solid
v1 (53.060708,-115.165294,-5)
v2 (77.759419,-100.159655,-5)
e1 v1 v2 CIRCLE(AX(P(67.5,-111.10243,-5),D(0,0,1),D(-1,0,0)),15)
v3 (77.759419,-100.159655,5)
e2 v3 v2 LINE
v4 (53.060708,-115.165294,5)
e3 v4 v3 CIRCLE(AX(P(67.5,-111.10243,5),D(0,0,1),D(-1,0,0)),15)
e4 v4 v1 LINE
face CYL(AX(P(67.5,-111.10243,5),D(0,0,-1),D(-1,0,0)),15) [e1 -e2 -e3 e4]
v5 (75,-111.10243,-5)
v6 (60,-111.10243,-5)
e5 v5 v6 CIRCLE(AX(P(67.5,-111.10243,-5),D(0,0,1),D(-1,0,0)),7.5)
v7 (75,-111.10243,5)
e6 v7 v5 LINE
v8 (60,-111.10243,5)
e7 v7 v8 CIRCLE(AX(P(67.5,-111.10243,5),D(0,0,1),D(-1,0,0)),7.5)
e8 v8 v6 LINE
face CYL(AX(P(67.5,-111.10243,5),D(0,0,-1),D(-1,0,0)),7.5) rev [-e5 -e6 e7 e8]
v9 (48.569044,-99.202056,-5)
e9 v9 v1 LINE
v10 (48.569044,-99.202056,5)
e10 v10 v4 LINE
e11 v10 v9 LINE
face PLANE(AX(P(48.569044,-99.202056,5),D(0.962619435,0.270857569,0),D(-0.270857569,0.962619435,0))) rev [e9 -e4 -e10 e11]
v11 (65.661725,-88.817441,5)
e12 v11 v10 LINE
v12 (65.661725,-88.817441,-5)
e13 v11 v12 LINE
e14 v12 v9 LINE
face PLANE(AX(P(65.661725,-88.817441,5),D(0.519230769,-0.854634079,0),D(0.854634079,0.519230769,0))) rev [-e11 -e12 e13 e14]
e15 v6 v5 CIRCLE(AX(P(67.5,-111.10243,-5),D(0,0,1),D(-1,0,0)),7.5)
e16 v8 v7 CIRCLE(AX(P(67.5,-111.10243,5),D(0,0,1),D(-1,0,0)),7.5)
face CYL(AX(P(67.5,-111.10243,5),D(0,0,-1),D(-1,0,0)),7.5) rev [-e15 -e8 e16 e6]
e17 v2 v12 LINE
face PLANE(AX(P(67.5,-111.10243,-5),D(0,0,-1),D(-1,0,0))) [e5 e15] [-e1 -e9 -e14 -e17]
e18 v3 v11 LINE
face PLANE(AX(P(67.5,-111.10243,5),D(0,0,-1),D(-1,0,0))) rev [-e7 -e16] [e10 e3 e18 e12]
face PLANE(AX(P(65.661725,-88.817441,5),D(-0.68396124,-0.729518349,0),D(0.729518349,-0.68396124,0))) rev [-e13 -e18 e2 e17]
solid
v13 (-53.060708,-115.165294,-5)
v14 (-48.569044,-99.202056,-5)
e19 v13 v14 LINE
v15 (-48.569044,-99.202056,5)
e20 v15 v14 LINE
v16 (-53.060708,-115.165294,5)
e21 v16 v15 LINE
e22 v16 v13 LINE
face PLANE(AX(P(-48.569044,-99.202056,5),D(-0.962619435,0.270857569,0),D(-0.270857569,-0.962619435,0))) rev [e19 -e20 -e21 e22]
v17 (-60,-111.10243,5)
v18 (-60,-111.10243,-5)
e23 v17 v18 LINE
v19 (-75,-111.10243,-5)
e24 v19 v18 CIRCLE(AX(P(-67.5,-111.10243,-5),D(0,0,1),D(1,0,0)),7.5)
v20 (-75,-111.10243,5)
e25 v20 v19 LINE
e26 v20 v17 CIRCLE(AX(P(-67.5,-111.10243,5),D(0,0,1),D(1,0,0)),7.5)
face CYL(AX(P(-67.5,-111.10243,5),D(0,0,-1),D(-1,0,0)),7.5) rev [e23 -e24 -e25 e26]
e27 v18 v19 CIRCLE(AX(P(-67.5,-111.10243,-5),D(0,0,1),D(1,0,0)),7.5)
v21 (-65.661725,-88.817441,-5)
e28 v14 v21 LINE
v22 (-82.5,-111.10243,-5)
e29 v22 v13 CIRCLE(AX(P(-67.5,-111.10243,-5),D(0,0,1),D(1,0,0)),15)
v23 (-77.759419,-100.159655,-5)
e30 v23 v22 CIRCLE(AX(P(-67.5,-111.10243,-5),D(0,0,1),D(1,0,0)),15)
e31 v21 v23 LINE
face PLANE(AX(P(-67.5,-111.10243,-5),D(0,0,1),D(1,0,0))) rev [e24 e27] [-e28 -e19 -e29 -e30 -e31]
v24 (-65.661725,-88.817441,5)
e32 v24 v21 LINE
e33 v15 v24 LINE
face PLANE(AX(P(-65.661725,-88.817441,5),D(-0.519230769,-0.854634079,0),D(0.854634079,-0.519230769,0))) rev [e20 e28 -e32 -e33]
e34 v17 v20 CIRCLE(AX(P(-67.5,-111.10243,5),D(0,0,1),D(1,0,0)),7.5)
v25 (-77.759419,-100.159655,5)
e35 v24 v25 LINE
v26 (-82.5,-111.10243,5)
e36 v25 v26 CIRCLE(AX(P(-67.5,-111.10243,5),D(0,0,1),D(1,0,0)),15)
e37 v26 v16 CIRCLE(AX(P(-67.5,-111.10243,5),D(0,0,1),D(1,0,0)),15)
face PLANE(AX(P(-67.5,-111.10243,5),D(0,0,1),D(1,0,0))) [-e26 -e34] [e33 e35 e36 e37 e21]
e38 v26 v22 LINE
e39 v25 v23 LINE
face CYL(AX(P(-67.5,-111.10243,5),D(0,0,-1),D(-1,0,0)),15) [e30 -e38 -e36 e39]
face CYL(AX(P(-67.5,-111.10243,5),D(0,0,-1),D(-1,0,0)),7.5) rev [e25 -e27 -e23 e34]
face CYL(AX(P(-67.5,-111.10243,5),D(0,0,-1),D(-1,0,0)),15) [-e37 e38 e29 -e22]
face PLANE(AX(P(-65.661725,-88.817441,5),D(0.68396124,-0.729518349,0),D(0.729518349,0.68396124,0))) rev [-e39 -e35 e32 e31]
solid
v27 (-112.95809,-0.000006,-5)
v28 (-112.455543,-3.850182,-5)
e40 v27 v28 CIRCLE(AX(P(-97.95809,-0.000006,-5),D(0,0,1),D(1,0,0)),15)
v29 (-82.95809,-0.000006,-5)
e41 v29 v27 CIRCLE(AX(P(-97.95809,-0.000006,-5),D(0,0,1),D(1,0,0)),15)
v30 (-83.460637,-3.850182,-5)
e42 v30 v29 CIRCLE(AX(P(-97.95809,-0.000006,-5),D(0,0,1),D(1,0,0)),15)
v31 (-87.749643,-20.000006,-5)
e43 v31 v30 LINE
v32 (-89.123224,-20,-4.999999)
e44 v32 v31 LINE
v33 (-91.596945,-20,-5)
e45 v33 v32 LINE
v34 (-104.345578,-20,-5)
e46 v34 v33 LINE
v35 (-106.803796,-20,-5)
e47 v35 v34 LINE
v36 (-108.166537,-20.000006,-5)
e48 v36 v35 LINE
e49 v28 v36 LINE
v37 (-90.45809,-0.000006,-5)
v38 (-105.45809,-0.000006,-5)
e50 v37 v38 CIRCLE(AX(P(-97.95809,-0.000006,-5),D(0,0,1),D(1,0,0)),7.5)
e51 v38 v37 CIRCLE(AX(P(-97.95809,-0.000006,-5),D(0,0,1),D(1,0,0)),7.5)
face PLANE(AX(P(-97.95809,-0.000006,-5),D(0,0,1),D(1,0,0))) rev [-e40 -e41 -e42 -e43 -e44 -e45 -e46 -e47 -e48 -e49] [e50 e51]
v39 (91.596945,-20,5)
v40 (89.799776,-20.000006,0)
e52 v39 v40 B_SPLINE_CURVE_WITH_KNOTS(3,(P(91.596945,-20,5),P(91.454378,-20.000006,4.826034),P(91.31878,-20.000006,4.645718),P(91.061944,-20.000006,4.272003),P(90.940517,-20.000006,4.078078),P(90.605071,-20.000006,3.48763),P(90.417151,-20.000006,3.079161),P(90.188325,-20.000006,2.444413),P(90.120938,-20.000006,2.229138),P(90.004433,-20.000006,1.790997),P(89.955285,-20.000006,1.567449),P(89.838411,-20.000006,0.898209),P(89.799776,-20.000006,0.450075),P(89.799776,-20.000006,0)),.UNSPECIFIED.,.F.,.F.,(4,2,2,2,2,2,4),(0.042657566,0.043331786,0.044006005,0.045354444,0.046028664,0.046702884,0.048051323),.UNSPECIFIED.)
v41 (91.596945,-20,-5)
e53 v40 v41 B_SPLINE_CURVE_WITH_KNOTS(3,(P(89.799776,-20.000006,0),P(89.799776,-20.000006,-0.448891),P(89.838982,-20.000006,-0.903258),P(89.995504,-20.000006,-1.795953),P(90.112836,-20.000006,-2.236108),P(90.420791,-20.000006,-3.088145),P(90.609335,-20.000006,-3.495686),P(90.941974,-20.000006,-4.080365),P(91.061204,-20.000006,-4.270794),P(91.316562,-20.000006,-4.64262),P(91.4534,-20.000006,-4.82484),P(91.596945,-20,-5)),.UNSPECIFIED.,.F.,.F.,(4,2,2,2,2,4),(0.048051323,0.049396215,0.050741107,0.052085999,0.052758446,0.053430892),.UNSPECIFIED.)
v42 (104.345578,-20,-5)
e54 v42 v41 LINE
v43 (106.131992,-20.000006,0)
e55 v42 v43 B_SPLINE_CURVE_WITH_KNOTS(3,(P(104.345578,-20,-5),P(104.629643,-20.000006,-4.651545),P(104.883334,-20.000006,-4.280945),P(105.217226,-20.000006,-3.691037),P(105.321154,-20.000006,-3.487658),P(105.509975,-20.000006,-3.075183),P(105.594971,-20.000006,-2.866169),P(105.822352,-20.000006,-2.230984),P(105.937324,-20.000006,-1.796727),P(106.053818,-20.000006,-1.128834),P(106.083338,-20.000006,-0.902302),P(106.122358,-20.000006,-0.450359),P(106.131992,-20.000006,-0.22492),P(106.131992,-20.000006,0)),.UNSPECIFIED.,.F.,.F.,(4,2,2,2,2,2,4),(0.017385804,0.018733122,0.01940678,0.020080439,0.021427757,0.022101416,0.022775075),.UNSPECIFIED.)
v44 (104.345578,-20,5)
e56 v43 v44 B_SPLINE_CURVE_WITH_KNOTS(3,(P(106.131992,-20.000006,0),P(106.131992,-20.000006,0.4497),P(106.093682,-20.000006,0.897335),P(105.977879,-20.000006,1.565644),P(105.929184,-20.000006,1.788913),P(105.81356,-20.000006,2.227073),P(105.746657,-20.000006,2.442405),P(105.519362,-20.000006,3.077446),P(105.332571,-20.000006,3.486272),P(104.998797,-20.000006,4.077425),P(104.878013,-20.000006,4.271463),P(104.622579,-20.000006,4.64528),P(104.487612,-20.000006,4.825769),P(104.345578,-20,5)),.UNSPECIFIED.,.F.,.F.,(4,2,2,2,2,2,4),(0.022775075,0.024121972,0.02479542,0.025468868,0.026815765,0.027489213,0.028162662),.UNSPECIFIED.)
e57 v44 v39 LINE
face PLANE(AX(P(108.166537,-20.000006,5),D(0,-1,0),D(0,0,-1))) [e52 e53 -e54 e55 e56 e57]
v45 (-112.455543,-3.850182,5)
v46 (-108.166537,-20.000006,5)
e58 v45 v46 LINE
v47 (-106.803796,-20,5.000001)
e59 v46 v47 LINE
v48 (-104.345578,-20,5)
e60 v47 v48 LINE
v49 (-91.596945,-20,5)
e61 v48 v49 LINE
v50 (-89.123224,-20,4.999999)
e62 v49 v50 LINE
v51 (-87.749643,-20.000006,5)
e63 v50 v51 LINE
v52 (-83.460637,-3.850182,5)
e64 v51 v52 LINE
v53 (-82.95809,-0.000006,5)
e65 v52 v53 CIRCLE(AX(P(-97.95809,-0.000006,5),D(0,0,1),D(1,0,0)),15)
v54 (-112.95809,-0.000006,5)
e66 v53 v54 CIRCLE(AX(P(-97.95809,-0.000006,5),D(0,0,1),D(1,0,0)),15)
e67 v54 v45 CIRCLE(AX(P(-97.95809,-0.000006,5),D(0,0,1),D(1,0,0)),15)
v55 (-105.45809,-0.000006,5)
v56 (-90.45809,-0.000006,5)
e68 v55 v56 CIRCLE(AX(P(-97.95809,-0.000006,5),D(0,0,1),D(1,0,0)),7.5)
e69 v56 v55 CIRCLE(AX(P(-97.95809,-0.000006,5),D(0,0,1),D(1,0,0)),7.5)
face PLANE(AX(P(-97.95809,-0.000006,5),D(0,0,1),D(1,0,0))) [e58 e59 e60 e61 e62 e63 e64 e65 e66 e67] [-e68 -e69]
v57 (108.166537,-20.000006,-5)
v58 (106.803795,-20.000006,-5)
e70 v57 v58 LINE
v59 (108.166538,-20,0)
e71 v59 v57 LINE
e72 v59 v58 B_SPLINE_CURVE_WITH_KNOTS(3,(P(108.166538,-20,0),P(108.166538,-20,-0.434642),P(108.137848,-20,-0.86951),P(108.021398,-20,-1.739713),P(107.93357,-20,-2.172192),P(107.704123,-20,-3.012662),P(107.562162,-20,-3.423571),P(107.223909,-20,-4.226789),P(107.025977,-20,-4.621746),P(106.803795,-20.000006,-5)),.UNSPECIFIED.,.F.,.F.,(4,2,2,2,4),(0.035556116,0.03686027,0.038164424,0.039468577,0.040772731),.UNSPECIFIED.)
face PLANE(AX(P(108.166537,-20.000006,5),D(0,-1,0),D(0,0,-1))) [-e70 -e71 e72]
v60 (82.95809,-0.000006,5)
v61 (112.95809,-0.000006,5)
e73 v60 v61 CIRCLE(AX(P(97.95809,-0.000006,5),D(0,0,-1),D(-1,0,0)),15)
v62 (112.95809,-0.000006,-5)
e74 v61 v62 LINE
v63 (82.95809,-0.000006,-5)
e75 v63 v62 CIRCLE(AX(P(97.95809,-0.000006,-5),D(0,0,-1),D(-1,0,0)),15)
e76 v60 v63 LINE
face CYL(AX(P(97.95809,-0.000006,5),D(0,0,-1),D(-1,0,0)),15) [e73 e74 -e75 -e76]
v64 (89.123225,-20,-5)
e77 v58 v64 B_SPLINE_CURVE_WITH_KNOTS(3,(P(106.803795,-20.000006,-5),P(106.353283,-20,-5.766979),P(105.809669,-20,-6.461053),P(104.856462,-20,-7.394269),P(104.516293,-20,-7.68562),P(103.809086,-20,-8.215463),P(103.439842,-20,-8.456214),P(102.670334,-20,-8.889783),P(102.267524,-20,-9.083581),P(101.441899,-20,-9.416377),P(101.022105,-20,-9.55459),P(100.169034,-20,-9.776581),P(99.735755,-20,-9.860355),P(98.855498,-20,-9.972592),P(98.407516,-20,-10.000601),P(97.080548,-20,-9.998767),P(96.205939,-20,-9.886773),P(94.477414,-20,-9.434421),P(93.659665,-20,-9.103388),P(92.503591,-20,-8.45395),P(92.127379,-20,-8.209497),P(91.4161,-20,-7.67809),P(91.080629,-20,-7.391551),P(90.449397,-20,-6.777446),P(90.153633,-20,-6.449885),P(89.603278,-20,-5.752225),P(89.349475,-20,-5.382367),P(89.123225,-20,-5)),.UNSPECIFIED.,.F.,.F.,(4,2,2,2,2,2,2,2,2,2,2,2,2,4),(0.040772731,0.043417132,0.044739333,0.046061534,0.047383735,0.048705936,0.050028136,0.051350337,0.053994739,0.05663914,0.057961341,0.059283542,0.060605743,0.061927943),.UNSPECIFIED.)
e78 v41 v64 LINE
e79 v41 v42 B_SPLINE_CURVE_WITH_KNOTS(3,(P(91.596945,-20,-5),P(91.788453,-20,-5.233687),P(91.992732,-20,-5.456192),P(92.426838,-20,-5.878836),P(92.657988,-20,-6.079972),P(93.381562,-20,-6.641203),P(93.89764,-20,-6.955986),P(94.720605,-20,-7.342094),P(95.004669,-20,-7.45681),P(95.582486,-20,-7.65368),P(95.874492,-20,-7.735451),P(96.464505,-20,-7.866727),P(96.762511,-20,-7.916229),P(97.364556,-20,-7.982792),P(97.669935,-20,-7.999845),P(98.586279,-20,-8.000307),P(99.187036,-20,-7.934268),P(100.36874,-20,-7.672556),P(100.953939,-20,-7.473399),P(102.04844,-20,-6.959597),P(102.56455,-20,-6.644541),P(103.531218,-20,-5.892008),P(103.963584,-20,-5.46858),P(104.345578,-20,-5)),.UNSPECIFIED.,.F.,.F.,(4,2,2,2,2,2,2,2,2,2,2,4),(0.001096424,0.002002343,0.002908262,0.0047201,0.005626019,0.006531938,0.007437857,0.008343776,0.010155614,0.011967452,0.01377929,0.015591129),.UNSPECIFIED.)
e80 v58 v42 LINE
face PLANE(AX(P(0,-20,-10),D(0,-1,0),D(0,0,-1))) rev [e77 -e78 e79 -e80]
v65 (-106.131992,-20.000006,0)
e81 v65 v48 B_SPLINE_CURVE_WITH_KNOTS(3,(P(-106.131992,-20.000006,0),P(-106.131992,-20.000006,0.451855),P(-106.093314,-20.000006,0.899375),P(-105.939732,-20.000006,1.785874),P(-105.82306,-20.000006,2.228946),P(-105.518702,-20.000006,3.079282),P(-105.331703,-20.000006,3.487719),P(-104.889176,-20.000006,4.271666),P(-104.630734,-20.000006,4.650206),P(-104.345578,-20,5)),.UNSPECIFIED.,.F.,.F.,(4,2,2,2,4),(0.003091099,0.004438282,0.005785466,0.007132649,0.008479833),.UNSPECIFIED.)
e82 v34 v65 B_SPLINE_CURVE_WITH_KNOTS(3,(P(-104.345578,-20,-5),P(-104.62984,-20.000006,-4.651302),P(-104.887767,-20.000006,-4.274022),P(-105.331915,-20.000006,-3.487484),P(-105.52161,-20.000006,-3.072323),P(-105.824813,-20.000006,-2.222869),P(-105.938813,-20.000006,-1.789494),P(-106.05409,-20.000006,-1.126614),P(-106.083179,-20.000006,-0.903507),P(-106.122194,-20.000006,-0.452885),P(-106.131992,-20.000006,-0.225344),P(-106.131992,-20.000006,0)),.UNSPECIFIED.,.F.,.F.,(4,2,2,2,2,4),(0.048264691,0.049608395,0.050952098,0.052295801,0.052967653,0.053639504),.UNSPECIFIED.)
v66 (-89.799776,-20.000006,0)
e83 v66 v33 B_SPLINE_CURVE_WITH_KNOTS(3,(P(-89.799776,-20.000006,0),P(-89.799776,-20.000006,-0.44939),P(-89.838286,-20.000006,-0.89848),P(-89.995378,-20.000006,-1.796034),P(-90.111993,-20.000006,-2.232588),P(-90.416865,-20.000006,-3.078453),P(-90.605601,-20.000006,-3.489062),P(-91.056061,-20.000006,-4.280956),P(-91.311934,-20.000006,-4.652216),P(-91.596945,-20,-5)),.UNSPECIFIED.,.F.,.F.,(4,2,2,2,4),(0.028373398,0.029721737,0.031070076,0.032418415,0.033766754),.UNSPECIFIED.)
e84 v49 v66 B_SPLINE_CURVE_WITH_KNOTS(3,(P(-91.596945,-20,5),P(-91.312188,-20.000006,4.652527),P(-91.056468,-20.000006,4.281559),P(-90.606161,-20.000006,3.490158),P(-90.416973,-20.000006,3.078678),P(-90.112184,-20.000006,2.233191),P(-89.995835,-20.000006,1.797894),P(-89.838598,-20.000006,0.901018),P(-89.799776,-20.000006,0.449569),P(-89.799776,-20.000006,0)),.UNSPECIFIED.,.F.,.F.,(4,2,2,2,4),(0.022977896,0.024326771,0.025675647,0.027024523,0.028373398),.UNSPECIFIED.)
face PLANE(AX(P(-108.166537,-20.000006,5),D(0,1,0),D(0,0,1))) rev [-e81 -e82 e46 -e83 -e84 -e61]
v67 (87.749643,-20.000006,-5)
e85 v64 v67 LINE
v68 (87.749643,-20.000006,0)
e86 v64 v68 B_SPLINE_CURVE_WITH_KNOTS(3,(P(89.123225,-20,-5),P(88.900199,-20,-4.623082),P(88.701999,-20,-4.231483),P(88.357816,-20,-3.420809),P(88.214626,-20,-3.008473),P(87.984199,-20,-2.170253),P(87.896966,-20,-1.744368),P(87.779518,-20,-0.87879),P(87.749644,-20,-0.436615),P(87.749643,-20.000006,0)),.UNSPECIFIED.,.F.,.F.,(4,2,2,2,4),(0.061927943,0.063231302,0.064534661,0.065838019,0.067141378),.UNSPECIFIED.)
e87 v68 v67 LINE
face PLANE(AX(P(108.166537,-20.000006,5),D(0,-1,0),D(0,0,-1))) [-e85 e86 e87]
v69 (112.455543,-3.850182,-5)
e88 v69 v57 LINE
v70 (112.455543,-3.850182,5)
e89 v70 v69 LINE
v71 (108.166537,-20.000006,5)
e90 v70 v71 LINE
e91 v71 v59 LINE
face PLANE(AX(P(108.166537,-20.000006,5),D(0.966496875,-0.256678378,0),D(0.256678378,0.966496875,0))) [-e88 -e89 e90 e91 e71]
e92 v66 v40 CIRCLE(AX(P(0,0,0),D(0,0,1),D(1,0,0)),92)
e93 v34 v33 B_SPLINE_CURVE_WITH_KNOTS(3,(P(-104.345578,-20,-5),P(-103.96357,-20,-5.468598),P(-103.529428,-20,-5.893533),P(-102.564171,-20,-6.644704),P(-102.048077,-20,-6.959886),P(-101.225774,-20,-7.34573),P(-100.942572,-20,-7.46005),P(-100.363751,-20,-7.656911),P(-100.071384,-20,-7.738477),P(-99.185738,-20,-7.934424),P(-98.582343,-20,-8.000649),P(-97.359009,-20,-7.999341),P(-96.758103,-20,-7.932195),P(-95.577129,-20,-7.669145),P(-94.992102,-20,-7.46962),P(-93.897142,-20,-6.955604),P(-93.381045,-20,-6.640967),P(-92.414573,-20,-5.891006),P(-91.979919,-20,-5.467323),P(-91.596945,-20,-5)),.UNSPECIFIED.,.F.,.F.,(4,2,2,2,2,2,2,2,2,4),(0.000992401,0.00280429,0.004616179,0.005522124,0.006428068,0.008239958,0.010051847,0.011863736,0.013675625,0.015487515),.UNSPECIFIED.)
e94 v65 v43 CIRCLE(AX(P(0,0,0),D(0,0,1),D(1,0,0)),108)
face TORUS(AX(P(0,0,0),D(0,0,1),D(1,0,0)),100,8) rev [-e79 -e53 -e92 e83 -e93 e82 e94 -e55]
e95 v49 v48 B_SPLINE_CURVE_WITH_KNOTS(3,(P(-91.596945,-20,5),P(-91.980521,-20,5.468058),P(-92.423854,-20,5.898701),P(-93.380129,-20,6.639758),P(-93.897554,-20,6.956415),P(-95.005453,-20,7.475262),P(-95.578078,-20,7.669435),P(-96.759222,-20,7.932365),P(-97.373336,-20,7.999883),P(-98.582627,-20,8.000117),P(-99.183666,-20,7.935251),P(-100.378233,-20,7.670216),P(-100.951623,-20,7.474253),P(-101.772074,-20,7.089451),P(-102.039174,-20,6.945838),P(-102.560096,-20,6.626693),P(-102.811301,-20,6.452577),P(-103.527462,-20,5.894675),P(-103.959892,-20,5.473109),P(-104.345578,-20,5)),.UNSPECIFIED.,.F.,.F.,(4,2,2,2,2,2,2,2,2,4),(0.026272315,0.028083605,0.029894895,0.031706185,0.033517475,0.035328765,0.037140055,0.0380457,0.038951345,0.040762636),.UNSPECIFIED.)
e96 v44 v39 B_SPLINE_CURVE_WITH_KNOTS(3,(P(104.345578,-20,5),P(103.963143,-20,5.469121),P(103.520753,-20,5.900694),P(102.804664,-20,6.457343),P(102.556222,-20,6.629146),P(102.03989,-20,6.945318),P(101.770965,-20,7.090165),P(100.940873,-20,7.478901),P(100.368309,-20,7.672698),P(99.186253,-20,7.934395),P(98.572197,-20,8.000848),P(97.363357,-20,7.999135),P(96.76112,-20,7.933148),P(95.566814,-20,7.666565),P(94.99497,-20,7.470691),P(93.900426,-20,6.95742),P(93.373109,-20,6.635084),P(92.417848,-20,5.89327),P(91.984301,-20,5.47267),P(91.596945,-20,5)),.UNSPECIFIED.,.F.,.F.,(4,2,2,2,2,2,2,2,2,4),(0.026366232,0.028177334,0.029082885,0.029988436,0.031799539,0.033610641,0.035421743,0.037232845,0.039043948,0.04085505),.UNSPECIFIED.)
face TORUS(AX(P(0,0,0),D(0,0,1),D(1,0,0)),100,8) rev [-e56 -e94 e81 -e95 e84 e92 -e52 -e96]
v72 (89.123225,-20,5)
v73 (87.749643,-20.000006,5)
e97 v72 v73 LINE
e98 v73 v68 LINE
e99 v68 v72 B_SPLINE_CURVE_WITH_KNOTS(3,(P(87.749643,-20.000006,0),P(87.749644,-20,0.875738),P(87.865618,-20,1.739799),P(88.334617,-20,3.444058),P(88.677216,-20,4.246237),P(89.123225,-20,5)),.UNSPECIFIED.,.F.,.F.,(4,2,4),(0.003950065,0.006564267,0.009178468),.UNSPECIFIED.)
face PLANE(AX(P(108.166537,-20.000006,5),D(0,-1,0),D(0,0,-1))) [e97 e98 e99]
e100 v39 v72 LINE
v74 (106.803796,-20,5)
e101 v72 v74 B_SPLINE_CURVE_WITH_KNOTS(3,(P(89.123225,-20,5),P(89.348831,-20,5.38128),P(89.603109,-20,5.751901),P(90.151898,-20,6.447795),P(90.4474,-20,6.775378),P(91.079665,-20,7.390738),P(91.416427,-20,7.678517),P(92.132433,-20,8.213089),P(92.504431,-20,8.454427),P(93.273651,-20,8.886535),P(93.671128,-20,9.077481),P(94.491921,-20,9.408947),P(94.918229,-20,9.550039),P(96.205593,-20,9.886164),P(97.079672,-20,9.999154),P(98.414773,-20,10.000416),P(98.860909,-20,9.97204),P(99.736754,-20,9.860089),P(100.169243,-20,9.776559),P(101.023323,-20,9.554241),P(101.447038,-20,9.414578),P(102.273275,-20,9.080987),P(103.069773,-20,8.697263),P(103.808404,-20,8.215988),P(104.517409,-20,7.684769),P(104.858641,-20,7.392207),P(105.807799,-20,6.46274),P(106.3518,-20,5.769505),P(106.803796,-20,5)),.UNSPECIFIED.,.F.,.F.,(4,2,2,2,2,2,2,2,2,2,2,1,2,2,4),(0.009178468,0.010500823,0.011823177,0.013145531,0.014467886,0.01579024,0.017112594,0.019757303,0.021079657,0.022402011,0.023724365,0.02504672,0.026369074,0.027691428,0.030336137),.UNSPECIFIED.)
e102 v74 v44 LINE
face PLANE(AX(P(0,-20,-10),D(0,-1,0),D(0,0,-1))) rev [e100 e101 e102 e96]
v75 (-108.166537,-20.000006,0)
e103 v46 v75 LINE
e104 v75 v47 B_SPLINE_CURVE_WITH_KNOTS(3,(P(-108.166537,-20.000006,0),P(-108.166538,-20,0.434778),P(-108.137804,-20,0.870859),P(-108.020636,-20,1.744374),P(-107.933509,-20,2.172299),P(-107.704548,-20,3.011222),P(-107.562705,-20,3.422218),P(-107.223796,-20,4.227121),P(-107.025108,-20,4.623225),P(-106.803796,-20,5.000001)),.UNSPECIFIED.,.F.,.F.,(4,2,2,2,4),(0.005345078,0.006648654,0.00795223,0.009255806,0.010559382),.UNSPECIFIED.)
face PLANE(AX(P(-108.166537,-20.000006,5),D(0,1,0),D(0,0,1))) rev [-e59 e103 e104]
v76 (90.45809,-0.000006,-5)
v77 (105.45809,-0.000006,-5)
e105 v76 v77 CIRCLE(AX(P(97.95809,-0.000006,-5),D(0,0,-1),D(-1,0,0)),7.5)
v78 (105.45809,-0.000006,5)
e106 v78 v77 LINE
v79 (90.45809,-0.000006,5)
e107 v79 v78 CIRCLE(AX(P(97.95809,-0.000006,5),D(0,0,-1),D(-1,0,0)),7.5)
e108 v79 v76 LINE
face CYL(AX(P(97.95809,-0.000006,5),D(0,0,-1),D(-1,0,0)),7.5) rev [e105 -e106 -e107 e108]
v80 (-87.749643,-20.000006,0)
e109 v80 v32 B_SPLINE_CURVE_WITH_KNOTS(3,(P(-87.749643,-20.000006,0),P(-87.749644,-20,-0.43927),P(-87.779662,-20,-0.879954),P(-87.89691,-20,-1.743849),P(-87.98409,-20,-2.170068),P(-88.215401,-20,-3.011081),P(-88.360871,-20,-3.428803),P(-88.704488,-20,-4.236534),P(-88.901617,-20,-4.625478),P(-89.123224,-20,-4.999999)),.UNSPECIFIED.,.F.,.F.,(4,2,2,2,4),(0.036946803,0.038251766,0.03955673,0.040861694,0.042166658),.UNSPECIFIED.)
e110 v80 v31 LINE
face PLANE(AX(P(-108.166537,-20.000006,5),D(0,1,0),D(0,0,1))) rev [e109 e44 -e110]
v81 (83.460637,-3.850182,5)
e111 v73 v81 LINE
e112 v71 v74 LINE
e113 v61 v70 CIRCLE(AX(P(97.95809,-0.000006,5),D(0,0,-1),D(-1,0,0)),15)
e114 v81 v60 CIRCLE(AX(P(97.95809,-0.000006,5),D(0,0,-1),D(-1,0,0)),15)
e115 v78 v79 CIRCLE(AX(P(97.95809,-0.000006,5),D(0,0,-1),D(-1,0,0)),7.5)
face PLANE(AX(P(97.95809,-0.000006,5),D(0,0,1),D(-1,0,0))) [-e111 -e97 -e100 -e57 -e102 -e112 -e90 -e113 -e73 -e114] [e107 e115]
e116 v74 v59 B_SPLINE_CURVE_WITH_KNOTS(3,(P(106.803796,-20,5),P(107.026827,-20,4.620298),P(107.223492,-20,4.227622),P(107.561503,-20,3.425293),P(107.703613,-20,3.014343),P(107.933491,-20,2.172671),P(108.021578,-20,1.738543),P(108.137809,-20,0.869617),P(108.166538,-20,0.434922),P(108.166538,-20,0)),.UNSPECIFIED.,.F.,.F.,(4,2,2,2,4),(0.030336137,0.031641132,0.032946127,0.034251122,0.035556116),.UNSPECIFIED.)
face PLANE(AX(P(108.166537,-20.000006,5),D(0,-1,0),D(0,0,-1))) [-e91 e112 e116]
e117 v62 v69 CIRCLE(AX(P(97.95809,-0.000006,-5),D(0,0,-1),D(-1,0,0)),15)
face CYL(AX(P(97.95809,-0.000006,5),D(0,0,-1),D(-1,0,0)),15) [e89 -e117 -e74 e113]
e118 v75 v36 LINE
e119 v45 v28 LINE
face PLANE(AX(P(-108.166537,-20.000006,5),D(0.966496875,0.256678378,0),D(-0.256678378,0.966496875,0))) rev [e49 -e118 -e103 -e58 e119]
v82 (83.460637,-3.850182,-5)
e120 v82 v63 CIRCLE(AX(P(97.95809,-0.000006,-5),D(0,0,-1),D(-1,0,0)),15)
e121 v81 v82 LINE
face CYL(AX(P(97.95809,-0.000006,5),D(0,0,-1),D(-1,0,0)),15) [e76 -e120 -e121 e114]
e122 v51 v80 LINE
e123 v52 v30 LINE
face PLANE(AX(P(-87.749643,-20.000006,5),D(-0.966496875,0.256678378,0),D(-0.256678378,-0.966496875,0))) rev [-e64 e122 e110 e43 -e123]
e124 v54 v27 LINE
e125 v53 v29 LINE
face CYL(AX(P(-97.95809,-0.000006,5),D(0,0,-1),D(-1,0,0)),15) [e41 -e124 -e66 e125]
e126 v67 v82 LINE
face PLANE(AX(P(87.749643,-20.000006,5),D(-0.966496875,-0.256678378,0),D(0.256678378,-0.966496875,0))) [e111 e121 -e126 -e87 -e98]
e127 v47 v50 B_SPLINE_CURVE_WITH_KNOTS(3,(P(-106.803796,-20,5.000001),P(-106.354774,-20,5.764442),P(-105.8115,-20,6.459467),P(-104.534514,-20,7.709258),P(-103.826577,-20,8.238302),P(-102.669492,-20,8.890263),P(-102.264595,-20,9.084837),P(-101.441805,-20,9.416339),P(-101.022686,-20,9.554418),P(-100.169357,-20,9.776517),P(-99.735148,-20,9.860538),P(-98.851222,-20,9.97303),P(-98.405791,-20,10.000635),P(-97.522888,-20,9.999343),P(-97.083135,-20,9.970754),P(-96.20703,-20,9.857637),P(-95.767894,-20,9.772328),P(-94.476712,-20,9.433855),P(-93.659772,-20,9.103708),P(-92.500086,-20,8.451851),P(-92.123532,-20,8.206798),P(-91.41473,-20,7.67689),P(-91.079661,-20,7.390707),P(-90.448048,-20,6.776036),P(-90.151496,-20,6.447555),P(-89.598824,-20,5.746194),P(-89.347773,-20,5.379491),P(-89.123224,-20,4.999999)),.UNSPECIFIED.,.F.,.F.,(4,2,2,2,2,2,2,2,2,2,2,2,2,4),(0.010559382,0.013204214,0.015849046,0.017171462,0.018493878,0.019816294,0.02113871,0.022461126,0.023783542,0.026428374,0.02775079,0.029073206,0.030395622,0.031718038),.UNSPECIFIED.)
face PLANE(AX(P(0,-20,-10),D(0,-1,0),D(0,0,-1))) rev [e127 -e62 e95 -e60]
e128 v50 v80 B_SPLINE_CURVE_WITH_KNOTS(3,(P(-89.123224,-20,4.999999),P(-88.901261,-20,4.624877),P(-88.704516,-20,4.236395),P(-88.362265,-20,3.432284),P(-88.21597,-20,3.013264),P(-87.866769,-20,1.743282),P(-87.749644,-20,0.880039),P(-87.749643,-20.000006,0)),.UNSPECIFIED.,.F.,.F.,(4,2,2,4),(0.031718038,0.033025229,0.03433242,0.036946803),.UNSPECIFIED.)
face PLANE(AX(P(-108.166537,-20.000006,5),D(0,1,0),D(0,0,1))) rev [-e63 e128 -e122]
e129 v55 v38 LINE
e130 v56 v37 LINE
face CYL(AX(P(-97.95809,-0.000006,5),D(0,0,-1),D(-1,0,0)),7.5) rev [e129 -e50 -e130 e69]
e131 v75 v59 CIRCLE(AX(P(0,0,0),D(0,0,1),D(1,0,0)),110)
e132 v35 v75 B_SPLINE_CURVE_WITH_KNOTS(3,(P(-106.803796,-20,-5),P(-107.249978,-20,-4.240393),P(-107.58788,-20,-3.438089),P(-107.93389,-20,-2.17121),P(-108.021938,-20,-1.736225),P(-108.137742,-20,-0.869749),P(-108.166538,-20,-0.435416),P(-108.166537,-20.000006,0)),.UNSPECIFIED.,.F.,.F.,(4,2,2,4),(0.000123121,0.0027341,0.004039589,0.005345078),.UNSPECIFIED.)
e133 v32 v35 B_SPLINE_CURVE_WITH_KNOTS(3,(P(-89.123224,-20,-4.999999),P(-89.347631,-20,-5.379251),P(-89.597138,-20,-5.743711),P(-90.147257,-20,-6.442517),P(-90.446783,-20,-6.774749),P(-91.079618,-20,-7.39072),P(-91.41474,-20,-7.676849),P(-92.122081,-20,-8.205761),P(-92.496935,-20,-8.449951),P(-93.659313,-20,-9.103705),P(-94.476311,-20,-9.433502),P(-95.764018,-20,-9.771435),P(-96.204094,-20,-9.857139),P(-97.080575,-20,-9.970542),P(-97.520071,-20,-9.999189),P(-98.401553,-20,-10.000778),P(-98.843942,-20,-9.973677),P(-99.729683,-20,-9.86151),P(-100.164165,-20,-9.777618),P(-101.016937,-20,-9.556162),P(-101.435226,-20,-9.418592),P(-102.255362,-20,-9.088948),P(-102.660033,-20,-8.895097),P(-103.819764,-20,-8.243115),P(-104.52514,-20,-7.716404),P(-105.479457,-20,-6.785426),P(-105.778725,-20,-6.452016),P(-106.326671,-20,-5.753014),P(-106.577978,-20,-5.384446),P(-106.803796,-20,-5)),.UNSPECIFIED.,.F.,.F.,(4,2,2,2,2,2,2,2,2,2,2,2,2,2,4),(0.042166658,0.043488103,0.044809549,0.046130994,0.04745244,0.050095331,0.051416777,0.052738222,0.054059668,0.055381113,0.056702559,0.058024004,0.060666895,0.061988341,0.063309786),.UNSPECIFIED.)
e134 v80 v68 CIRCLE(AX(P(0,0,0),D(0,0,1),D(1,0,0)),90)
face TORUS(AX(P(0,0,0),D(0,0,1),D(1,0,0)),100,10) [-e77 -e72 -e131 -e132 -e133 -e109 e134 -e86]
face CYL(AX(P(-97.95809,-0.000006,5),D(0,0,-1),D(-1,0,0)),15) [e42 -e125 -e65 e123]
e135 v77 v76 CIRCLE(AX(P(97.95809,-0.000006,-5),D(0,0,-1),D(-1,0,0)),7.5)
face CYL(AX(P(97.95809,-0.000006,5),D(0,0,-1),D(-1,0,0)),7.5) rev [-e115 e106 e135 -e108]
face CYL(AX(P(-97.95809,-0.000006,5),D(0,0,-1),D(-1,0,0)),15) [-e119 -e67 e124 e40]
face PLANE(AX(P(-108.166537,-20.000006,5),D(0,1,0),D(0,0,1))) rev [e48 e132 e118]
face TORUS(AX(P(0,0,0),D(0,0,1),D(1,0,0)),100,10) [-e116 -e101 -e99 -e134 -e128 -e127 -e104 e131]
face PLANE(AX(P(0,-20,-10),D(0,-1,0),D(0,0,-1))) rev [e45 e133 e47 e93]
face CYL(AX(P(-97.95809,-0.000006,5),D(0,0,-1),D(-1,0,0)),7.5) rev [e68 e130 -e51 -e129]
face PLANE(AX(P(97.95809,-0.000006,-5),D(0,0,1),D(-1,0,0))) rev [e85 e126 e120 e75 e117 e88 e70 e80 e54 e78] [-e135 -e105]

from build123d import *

# Parameters (mm, degrees)
SKETCH_2_R               = 10
SKETCH_2_R_2             = 8
CUT_EXTRUDE_1_DEPTH      = 156.884572829
CUT_EXTRUDE_1_DEPTH_BACK = 156.884572829
SKETCH_4_R               = 7.5
EXTRUDE_1_DEPTH          = 5
SKETCH_5_R               = 7.5
EXTRUDE_2_DEPTH          = 5
EXTRUDE_2_2_DEPTH        = 5


with BuildPart() as part:
    # 扫描1: sweep along a path in 草图1
    with BuildLine(Plane.XY) as sweep_1_path:
        CenterArc((0, 0), 100, 0, 360)
    # 草图2 → 扫描1 (sweep)
    with BuildSketch(Plane(origin=(0, 0, 0), x_dir=(0, 0, -1), z_dir=(1, 0, 0))):
        with Locations((0, -100)):
            Circle(SKETCH_2_R)
        with Locations((0, -100)):
            Circle(SKETCH_2_R_2, mode=Mode.SUBTRACT)
    sweep(path=sweep_1_path.line)

    # 草图3 → 切除-拉伸1 (cut, two sides: drawn at the far end of the back side and taken through both)
    with BuildSketch(Plane.XY.offset(-CUT_EXTRUDE_1_DEPTH_BACK)):
        Polygon((-124.821104754, -20), (0, -20), (127.823184446, -20), (127.823184446, 142.660997567), (-124.821104754, 142.660997567), align=None)
    extrude(amount=CUT_EXTRUDE_1_DEPTH + CUT_EXTRUDE_1_DEPTH_BACK, mode=Mode.SUBTRACT)

    # 草图4 → 凸台-拉伸1 (add, symmetric)
    with BuildSketch(Plane.XY):
        with BuildLine():
            Line((-108.166537158, -20.000005979), (-112.455542967, -3.850181648))
            ThreePointArc((-112.455542967, -3.850181648), (-97.958089835, 14.999994021), (-83.460636703, -3.850181648))
            Line((-83.460636703, -3.850181648), (-87.749642511, -20.000005979))
            Line((-87.749642511, -20.000005979), (-108.166537158, -20.000005979))
        make_face()
        with Locations((-97.958089835, -5.979e-06)):
            Circle(SKETCH_4_R, mode=Mode.SUBTRACT)
    extrude_1 = extrude(amount=EXTRUDE_1_DEPTH, both=True)

    # 镜向1: 凸台-拉伸1 across plane
    add(extrude_1.mirror(Plane(origin=(0, 0, 0), x_dir=(0, 0, 1), z_dir=(1, 0, 0))))


with BuildPart() as body_2:
    # 草图5 → 凸台-拉伸2 (new, symmetric)
    with BuildSketch(Plane.XY):
        with BuildLine():
            Line((-65.661725401, -88.817440952), (-48.56904383, -99.202056337))
            Line((-48.56904383, -99.202056337), (-53.06070847, -115.165293752))
            ThreePointArc((-53.06070847, -115.165293752), (-75.288461538, -123.921941395), (-77.759418607, -100.159654982))
            Line((-77.759418607, -100.159654982), (-65.661725401, -88.817440952))
        make_face()
        with Locations((-67.5, -111.102430216)):
            Circle(SKETCH_5_R, mode=Mode.SUBTRACT)
    extrude(amount=EXTRUDE_2_DEPTH, both=True)


with BuildPart() as body_3:
    # 草图5 → Extrude 2 2 (new, symmetric)
    with BuildSketch(Plane.XY):
        with BuildLine():
            Line((65.661725401, -88.817440952), (77.759418607, -100.159654982))
            ThreePointArc((77.759418607, -100.159654982), (75.288461538, -123.921941395), (53.06070847, -115.165293752))
            Line((53.06070847, -115.165293752), (48.56904383, -99.202056337))
            Line((48.56904383, -99.202056337), (65.661725401, -88.817440952))
        make_face()
        with Locations(Location((67.5, -111.102430216, 0), (0, 0, 180))):
            Circle(SKETCH_5_R, mode=Mode.SUBTRACT)
    extrude(amount=EXTRUDE_2_2_DEPTH, both=True)


solid = Compound([part.part, body_2.part, body_3.part])
